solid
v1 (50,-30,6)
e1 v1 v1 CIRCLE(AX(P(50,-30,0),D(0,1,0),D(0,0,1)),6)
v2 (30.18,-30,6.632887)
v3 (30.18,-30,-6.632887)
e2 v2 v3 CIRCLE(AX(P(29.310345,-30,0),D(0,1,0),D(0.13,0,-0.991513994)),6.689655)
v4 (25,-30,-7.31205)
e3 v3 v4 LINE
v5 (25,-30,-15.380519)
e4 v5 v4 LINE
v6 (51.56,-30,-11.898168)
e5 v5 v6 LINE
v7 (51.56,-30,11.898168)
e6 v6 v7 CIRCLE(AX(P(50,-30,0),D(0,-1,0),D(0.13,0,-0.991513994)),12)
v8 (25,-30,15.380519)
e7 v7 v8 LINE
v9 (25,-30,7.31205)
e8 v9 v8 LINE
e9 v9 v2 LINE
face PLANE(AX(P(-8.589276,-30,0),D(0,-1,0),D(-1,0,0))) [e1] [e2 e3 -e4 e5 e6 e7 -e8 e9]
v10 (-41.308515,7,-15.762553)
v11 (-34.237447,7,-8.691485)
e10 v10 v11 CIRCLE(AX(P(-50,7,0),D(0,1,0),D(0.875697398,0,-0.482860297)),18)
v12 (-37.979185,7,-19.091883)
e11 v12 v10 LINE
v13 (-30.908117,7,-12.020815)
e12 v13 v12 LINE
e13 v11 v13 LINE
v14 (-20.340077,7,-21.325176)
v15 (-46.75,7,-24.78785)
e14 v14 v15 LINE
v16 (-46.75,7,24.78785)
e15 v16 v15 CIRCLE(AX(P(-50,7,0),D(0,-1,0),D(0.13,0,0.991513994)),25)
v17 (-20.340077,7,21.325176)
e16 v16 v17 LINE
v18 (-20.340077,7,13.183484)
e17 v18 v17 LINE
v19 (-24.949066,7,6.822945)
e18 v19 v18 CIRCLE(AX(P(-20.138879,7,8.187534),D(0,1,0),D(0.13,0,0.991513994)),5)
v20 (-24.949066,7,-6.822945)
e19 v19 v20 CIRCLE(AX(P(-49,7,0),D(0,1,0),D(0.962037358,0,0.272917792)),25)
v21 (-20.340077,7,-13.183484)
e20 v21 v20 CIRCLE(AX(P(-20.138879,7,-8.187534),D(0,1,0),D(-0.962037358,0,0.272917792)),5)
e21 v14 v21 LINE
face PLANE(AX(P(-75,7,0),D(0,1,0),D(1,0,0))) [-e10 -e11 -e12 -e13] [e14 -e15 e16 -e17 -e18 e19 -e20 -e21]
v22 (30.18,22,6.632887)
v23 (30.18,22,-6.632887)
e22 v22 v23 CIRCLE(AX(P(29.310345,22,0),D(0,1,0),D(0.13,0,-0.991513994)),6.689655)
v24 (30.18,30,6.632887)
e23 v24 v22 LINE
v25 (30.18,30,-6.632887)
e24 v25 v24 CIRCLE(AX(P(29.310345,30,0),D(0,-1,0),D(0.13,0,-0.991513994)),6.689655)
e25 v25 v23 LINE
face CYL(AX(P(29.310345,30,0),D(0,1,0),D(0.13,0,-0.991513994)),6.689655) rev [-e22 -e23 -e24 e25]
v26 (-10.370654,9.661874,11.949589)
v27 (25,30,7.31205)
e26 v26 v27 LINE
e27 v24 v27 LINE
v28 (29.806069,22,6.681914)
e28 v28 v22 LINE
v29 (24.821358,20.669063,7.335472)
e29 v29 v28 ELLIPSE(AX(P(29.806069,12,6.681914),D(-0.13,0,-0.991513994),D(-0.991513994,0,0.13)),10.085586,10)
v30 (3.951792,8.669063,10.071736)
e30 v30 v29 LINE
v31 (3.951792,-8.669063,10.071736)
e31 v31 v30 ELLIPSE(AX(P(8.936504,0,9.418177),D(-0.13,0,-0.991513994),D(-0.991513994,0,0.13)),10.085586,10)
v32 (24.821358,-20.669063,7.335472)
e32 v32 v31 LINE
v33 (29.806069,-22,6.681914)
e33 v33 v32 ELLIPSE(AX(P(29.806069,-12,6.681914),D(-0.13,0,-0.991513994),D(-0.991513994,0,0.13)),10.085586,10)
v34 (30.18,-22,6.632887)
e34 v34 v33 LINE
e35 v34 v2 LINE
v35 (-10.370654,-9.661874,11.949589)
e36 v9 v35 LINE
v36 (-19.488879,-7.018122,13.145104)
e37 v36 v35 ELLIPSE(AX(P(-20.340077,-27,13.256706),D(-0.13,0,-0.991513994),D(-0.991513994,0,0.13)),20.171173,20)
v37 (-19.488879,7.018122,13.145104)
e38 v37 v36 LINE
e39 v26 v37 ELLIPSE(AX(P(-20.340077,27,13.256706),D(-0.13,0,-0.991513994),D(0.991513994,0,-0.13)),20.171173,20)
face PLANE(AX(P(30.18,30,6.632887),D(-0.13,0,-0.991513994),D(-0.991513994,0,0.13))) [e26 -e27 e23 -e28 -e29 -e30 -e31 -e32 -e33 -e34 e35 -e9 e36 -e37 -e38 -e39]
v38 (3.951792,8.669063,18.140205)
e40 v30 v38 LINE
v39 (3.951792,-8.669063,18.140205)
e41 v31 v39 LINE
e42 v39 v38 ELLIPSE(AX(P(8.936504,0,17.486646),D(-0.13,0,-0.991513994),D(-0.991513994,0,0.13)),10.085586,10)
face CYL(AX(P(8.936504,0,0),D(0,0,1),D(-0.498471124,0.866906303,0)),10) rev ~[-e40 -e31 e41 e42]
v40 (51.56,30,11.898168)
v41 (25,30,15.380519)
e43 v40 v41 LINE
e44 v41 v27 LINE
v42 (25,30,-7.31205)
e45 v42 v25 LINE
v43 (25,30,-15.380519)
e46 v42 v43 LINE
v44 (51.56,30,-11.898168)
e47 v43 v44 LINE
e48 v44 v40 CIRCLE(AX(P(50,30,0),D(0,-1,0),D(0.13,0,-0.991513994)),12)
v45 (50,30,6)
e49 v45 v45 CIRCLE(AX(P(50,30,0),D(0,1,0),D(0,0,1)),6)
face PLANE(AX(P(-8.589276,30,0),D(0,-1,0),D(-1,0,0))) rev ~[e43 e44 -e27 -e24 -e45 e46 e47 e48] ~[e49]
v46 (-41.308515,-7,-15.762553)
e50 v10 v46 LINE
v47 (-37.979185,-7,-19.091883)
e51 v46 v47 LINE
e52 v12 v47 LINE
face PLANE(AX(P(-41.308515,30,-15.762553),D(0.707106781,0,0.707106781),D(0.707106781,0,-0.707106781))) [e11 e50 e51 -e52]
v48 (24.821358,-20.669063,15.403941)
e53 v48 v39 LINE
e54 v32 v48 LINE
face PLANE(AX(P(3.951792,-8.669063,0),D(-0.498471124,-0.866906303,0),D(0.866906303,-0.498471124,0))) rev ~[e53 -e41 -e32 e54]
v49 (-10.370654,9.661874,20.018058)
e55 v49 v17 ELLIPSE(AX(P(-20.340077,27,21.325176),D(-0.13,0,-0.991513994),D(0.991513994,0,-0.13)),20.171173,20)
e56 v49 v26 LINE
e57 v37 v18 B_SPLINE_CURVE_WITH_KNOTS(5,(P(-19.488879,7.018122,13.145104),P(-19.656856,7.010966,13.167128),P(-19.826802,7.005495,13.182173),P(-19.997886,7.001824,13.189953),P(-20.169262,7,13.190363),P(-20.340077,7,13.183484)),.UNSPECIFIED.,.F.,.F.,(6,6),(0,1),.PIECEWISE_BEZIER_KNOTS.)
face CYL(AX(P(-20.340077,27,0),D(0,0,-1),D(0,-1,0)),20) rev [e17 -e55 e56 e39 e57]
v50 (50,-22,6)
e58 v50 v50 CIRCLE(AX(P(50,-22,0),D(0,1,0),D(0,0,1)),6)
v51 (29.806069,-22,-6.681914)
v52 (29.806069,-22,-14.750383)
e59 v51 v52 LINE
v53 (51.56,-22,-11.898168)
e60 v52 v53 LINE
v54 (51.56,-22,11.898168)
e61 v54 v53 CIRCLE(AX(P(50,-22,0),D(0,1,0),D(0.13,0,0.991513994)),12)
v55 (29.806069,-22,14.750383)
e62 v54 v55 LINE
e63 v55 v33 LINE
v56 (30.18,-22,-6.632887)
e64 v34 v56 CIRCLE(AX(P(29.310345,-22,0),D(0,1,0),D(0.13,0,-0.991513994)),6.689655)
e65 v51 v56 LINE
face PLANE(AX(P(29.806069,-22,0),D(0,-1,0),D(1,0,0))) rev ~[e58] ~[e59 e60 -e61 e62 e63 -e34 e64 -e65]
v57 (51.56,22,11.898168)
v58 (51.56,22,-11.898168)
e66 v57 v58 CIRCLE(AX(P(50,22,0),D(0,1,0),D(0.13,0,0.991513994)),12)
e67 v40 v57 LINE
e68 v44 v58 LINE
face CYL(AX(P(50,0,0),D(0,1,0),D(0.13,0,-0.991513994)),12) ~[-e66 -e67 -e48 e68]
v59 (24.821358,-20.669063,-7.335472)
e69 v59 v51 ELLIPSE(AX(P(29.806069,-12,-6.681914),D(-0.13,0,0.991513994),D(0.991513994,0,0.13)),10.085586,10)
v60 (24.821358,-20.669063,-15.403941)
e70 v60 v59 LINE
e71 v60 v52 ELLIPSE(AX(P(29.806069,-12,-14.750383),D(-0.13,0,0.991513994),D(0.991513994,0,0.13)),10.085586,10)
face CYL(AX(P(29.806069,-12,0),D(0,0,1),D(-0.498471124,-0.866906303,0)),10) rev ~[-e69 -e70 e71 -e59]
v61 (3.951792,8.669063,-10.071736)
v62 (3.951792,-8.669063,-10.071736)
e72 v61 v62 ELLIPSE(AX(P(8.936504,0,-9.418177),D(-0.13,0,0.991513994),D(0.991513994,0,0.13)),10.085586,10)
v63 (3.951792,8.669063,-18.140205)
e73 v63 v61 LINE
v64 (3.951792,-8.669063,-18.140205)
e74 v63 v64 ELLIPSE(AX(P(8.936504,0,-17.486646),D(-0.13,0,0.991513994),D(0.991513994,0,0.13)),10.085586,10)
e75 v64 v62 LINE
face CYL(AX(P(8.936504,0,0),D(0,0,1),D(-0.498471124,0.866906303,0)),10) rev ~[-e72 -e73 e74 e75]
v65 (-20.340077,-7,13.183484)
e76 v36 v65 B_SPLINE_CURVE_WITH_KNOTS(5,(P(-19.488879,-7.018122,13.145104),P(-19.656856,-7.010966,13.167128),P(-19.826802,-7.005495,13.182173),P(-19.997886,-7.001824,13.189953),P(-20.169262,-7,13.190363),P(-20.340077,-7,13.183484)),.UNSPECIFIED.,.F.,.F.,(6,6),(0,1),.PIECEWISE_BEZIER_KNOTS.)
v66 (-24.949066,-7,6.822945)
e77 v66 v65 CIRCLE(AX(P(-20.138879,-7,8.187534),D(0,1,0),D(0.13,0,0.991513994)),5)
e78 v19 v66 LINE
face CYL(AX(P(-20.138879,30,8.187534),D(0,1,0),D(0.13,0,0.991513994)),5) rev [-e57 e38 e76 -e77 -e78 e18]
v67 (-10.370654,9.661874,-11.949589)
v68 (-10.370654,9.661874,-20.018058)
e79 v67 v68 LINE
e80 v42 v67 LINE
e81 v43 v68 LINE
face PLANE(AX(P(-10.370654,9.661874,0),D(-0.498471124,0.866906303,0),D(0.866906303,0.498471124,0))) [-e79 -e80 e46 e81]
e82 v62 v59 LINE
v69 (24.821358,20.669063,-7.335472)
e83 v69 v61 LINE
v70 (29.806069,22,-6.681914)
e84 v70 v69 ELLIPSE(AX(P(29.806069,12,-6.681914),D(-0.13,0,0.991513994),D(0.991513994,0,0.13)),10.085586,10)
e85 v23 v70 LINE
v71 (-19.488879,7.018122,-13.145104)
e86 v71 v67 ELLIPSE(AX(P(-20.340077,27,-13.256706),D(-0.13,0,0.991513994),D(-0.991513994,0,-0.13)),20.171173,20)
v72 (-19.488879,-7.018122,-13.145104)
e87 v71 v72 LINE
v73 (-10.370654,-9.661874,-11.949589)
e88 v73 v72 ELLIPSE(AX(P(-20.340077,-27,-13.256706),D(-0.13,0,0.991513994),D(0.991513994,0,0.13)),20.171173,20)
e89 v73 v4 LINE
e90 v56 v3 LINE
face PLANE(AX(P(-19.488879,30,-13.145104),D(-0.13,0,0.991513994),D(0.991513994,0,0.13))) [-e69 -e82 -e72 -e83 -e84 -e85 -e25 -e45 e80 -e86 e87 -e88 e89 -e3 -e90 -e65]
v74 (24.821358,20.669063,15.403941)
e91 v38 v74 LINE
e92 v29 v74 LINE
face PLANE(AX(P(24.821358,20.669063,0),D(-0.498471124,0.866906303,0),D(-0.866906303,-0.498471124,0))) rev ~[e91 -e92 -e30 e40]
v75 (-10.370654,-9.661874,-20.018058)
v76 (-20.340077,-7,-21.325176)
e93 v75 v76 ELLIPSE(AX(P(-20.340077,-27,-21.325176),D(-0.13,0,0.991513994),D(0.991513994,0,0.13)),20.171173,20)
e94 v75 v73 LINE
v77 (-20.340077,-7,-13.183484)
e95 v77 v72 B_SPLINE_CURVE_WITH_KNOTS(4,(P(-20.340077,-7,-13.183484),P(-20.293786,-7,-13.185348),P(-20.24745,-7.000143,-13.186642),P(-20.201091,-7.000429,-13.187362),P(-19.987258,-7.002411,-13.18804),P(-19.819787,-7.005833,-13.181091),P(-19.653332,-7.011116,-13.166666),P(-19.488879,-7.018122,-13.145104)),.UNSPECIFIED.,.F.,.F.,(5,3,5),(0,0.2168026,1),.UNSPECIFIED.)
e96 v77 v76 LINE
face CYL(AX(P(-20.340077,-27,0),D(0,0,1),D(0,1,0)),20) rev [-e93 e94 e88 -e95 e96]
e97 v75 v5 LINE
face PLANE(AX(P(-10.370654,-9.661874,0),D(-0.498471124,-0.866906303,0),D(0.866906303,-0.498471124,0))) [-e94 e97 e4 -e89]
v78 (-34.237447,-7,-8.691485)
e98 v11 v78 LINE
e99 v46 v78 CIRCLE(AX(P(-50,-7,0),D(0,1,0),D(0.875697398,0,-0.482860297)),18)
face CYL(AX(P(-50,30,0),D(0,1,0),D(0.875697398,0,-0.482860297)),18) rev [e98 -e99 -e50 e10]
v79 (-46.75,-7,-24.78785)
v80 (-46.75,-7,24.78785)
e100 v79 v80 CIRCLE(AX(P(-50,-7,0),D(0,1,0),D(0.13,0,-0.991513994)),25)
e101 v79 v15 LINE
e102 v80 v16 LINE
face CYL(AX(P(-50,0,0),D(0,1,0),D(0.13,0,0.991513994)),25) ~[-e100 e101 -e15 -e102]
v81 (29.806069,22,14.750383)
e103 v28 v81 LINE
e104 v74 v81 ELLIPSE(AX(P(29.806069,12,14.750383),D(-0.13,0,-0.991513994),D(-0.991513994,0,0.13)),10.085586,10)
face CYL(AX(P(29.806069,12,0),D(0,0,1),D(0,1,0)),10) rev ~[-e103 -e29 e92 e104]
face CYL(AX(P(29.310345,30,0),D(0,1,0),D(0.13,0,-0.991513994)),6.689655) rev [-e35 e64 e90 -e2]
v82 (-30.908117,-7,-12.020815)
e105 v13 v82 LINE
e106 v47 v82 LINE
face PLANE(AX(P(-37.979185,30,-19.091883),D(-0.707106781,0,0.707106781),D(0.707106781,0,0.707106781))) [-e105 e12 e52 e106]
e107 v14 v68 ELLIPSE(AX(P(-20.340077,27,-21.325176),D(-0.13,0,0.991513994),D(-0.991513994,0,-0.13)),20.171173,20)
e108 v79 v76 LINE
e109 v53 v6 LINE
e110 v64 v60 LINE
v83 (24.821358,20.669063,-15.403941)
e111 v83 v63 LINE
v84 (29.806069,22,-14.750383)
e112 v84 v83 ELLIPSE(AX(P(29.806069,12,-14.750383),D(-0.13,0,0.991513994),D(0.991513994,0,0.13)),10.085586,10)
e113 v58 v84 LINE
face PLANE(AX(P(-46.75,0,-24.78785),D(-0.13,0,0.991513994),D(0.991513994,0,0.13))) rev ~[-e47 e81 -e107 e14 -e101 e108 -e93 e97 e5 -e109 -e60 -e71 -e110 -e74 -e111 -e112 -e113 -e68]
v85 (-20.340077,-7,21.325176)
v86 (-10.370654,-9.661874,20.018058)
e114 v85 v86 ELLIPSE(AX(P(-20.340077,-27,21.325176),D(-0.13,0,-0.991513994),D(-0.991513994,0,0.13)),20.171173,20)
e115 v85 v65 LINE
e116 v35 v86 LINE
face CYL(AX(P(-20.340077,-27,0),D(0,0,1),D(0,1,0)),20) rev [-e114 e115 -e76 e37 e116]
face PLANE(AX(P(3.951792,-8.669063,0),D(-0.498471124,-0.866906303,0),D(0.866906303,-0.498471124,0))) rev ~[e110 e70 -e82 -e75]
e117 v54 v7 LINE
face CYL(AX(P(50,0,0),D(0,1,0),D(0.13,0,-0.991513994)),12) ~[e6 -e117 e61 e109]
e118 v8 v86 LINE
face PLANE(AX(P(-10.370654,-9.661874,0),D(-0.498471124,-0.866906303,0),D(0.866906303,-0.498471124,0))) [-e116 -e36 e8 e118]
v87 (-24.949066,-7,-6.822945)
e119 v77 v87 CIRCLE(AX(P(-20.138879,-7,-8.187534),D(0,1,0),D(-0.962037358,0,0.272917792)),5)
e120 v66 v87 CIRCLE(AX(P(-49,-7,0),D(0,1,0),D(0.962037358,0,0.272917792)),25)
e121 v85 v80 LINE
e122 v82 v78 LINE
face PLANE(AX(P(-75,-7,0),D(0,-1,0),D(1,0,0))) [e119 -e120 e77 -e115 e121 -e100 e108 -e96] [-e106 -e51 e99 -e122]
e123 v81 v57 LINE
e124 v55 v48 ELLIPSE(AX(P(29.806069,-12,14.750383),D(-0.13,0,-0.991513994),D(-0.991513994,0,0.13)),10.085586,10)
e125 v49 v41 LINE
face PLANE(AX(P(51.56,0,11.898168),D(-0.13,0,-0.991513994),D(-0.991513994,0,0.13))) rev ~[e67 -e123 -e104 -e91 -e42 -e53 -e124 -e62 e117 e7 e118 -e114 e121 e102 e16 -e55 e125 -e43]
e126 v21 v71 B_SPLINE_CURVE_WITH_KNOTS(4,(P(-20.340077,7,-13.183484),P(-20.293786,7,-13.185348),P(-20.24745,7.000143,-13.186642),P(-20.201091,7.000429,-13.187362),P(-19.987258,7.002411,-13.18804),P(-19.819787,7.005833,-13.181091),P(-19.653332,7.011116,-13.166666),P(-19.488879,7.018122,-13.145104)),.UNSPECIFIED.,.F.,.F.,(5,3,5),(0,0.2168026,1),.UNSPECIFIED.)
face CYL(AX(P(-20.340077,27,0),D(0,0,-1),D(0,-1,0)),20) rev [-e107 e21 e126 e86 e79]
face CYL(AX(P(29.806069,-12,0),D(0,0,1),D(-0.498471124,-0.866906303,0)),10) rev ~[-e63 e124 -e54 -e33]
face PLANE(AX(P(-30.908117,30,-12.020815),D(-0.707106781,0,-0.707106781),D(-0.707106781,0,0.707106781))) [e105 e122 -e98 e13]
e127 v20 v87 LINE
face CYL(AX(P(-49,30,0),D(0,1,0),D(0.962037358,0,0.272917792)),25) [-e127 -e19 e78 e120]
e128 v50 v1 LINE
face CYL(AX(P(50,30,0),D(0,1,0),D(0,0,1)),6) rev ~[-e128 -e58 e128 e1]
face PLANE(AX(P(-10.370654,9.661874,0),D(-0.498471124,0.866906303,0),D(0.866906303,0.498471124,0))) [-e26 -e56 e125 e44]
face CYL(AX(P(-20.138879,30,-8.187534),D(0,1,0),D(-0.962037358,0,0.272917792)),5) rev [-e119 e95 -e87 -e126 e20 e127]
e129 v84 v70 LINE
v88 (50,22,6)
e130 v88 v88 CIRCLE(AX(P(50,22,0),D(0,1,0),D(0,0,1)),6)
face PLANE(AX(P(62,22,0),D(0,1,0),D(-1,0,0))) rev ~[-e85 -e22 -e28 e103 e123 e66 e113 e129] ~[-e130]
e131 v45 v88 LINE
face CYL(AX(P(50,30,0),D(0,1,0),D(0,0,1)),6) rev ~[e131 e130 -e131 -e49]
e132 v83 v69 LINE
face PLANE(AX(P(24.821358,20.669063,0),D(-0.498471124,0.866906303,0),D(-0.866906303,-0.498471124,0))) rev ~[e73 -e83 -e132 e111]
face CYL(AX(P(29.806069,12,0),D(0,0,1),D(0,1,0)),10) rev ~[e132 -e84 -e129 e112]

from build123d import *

# Parameters (mm, degrees)
LEVER_BLANK_DEPTH             = 30
HUB_BORE_36_WITH_KEYWAY_DEPTH = 100.247166206
HOLE_12_SKETCH_R              = 6
HOLE_12_DEPTH                 = 100.247166206
RELIEF_SLOT_DEPTH             = 100.247166206
FORK_OUTLINE_CUT_DEPTH        = 30
ARM_LIGHTENING_WINDOWS_DEPTH  = 30


with BuildPart() as part:
    # Side Profile Sketch → Lever Blank (new, symmetric)
    with BuildSketch(Plane(origin=(0, 0, 0), x_dir=(1, 0, 0), z_dir=(0, 1, 0))):
        with BuildLine():
            Line((-46.75, 24.787849846), (51.56, 11.898167926))
            ThreePointArc((51.56, 11.898167926), (62, 0), (51.56, -11.898167926))
            Line((51.56, -11.898167926), (-46.75, -24.787849846))
            ThreePointArc((-46.75, -24.787849846), (-75, 0), (-46.75, 24.787849846))
        make_face()
    extrude(amount=LEVER_BLANK_DEPTH, both=True)

    # Hub Bore Sketch → Hub Bore Ø36 with Keyway (cut, through all)
    with BuildSketch(Plane(origin=(0, 30, 0), x_dir=(1, 0, 0), z_dir=(0, 1, 0))):
        with BuildLine():
            Line((-41.308514645, 15.762553167), (-37.97918472, 19.091883092))
            Line((-37.97918472, 19.091883092), (-30.908116908, 12.02081528))
            Line((-30.908116908, 12.02081528), (-34.237446833, 8.691485355))
            ThreePointArc((-34.237446833, 8.691485355), (-62.727922061, -12.727922061), (-41.308514645, 15.762553167))
        make_face()
    extrude(amount=-HUB_BORE_36_WITH_KEYWAY_DEPTH, mode=Mode.SUBTRACT)

    # Hole Ø12 Sketch → Hole Ø12 (cut, through all)
    with BuildSketch(Plane(origin=(0, 30, 0), x_dir=(1, 0, 0), z_dir=(0, 1, 0))):
        with Locations(Location((50, 0, 0), (0, 0, 270))):
            Circle(HOLE_12_SKETCH_R)
    extrude(amount=-HOLE_12_DEPTH, mode=Mode.SUBTRACT)

    # Relief Slot Sketch → Relief Slot (cut, through all)
    with BuildSketch(Plane(origin=(0, 30, 0), x_dir=(1, 0, 0), z_dir=(0, 1, 0))):
        with BuildLine():
            Line((-19.488879252, 13.145103734), (30.18, 6.632886717))
            ThreePointArc((30.18, 6.632886717), (36, 0), (30.18, -6.632886717))
            Line((30.18, -6.632886717), (-19.488879252, -13.145103734))
            ThreePointArc((-19.488879252, -13.145103734), (-23.922952707, -11.455681264), (-24.949066043, -6.822944804))
            ThreePointArc((-24.949066043, -6.822944804), (-24, 0), (-24.949066043, 6.822944804))
            ThreePointArc((-24.949066043, 6.822944804), (-23.922952707, 11.455681264), (-19.488879252, 13.145103734))
        make_face()
    extrude(amount=-RELIEF_SLOT_DEPTH, mode=Mode.SUBTRACT)

    # Fork Outline Sketch → Fork Outline Cut (cut, symmetric)
    with BuildSketch(Plane.XY):
        with BuildLine():
            Line((-75, 30), (-75, 7))
            Line((-75, 7), (-20.340076505, 7))
            ThreePointArc((-20.340076505, 7), (-15.180741335, 7.676924142), (-10.370654019, 9.661873939))
            Line((-10.370654019, 9.661873939), (25, 30))
            Line((25, 30), (-75, 30))
        make_face()
        with BuildLine():
            Line((-75, -30), (-75, -7))
            Line((-75, -7), (-20.340076505, -7))
            ThreePointArc((-20.340076505, -7), (-15.180741335, -7.676924142), (-10.370654019, -9.661873939))
            Line((-10.370654019, -9.661873939), (25, -30))
            Line((25, -30), (-75, -30))
        make_face()
    extrude(amount=FORK_OUTLINE_CUT_DEPTH, both=True, mode=Mode.SUBTRACT)

    # Arm Windows Sketch → Arm Lightening Windows (cut, symmetric)
    with BuildSketch(Plane.XY):
        with BuildLine():
            Line((62, 22), (29.806068854, 22))
            ThreePointArc((29.806068854, 22), (27.226401269, 21.661537929), (24.821357612, 20.669063031))
            Line((24.821357612, 20.669063031), (3.951792394, 8.669063031))
            ThreePointArc((3.951792394, 8.669063031), (-1.063496363, 0), (3.951792394, -8.669063031))
            Line((3.951792394, -8.669063031), (24.821357612, -20.669063031))
            ThreePointArc((24.821357612, -20.669063031), (27.226401269, -21.661537929), (29.806068854, -22))
            Line((29.806068854, -22), (62, -22))
            Line((62, -22), (62, 22))
        make_face()
    extrude(amount=ARM_LIGHTENING_WINDOWS_DEPTH, both=True, mode=Mode.SUBTRACT)


solid = part.part
